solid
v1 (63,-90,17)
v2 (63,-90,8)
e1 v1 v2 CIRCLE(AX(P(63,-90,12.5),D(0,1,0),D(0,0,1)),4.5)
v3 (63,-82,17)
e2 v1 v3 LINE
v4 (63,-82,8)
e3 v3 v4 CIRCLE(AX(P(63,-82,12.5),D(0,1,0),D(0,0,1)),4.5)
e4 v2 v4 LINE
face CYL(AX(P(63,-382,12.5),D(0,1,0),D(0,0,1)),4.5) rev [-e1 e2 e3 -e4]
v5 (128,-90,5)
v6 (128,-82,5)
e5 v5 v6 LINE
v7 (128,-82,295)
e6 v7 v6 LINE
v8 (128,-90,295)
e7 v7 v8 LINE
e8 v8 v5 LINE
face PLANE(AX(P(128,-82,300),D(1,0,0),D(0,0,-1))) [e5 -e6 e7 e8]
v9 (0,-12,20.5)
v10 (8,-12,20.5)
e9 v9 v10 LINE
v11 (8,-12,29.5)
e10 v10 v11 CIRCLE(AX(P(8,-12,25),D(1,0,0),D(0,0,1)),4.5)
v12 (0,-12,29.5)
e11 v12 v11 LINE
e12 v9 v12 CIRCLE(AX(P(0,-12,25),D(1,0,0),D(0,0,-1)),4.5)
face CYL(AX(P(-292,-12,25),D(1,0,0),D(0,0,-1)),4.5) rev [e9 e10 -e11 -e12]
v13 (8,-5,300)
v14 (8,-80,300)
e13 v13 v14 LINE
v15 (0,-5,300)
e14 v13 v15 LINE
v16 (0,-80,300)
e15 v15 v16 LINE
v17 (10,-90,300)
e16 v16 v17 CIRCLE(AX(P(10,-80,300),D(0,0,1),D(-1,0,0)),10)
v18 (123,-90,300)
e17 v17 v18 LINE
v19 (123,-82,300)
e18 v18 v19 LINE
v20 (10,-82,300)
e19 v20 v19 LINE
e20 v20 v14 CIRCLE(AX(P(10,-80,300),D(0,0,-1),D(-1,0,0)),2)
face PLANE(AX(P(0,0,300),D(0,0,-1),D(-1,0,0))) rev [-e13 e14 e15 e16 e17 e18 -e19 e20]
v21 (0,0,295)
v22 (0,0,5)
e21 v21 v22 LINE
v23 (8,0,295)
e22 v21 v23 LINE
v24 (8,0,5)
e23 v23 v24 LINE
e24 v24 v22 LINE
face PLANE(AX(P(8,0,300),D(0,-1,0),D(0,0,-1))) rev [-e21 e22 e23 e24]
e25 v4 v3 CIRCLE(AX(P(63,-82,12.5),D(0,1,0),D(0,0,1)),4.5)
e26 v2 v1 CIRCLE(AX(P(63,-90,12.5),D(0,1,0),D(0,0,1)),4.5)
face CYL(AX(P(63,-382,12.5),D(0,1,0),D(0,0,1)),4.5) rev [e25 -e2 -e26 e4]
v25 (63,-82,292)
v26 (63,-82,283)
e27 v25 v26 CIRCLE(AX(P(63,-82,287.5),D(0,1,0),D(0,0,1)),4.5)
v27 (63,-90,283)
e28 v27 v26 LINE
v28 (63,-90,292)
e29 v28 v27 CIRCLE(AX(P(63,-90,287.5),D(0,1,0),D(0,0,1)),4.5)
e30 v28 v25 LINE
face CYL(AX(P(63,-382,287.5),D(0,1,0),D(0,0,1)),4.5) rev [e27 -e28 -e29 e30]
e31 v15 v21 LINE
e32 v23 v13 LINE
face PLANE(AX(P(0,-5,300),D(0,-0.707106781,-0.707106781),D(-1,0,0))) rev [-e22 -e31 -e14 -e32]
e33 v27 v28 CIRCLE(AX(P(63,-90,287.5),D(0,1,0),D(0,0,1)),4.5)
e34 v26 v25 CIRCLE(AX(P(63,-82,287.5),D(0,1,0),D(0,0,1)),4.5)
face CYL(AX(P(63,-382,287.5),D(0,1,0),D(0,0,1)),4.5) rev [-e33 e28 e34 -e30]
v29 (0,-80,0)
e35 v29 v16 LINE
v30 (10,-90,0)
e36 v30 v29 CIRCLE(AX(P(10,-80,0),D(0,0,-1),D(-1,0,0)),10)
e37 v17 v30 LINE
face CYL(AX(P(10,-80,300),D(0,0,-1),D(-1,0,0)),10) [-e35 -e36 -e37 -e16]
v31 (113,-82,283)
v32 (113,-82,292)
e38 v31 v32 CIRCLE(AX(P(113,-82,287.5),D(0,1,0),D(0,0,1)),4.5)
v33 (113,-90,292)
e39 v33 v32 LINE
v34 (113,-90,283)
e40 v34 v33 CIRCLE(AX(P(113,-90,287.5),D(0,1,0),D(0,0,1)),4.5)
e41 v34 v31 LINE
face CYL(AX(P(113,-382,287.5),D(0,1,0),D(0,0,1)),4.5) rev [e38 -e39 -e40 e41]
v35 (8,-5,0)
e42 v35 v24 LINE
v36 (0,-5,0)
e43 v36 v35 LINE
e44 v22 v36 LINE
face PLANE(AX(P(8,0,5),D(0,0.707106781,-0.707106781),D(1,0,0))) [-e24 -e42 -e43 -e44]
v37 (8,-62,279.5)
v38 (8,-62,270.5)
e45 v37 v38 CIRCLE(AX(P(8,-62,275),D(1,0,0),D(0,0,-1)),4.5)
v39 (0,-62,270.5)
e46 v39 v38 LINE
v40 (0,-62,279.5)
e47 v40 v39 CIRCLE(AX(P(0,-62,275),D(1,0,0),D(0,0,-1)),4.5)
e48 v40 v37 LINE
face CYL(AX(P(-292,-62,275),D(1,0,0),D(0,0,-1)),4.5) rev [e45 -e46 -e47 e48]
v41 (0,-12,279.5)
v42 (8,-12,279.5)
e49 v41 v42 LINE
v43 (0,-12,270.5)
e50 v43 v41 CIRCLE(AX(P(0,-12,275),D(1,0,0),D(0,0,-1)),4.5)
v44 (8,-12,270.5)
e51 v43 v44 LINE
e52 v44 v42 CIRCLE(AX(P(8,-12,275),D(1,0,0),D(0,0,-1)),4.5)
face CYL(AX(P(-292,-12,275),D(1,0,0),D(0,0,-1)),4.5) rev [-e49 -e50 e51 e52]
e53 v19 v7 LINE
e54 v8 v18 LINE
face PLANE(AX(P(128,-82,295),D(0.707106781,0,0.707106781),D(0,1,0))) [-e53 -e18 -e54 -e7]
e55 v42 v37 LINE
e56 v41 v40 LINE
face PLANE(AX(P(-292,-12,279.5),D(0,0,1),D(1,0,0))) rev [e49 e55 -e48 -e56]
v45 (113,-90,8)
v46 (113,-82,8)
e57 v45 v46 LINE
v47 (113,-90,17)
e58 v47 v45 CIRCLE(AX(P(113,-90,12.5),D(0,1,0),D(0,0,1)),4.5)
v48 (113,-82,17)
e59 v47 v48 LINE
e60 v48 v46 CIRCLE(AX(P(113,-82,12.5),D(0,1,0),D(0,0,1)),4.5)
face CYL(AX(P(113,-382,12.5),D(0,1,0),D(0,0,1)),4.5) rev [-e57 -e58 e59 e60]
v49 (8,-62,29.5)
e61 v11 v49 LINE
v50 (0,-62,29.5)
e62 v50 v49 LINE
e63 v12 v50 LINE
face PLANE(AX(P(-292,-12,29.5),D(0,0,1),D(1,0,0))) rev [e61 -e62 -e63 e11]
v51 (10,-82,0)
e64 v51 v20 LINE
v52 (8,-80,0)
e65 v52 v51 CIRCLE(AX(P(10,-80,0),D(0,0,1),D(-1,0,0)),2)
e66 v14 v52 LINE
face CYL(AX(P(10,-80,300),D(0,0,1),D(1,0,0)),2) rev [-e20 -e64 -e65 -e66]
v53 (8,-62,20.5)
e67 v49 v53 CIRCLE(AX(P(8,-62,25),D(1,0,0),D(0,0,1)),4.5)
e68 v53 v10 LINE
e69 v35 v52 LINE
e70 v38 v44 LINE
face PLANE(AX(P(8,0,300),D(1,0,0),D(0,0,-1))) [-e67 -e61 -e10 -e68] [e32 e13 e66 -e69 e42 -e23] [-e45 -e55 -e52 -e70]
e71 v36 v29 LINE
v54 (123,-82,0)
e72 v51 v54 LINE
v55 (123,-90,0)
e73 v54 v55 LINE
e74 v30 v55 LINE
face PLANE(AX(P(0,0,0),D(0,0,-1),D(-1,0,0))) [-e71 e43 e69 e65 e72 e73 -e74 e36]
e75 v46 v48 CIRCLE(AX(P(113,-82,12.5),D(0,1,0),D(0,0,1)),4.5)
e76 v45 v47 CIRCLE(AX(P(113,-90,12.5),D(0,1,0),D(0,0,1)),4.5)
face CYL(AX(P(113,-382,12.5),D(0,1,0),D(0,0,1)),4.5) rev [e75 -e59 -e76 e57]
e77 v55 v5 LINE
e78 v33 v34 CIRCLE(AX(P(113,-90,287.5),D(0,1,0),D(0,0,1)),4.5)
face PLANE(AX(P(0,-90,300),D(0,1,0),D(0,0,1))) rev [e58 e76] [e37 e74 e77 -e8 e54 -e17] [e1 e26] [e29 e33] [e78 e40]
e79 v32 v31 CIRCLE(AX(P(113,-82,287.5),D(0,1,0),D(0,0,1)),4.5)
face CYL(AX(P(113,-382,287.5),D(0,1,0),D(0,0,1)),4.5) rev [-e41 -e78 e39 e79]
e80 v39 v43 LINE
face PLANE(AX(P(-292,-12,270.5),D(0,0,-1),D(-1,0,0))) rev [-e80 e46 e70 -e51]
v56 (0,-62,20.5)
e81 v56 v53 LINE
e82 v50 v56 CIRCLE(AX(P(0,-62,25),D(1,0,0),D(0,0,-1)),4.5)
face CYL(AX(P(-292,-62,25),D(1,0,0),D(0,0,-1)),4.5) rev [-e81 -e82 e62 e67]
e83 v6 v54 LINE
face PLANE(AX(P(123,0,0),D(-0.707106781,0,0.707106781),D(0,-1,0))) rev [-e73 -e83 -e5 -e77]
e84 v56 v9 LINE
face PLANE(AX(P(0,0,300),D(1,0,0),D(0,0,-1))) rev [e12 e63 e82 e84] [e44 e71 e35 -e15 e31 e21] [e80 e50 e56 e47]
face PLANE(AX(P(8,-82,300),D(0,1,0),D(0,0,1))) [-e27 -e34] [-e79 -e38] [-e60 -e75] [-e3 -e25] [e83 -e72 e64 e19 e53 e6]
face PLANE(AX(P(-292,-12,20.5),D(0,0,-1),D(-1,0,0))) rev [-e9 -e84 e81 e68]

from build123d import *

# Parameters (mm, degrees)
BOSS_EXTRUDE1_DEPTH = 300
SKETCH2_R           = 4.5
CUT_EXTRUDE1_DEPTH  = 300
CUT_EXTRUDE2_DEPTH  = 300
CHAMFER1_SIZE       = 5
FILLET1_R           = 2
FILLET2_R           = 10


with BuildPart() as part:
    # Sketch1 → Boss-Extrude1 (new body)
    with BuildSketch(Plane.XY):
        Polygon((0, 0), (0, -90), (128, -90), (128, -82), (8, -82), (8, 0), align=None)
    extrude(amount=BOSS_EXTRUDE1_DEPTH)

    # Sketch2 → Cut-Extrude1 (cut)
    with BuildSketch(Plane(origin=(0, -82, 0), x_dir=(1, 0, 0), z_dir=(0, 1, 0))):
        with Locations(Location((63, -12.5, 0), (0, 0, 270))):
            Circle(SKETCH2_R)
        with Locations(Location((113, -12.5, 0), (0, 0, 270))):
            Circle(SKETCH2_R)
        with Locations(Location((63, -287.5, 0), (0, 0, 270))):
            Circle(SKETCH2_R)
        with Locations(Location((113, -287.5, 0), (0, 0, 270))):
            Circle(SKETCH2_R)
    extrude(amount=-CUT_EXTRUDE1_DEPTH, mode=Mode.SUBTRACT)

    # Sketch3 → Cut-Extrude2 (cut)
    with BuildSketch(Plane(origin=(8, 0, 0), x_dir=(0, 0, -1), z_dir=(1, 0, 0))):
        with BuildLine():
            Line((-270.5, -12), (-270.5, -62))
            ThreePointArc((-270.5, -62), (-275, -66.5), (-279.5, -62))
            Line((-279.5, -62), (-279.5, -12))
            ThreePointArc((-279.5, -12), (-275, -7.5), (-270.5, -12))
        make_face()
        with BuildLine():
            Line((-29.5, -12), (-29.5, -62))
            ThreePointArc((-29.5, -62), (-25, -66.5), (-20.5, -62))
            Line((-20.5, -62), (-20.5, -12))
            ThreePointArc((-20.5, -12), (-25, -7.5), (-29.5, -12))
        make_face()
    extrude(amount=-CUT_EXTRUDE2_DEPTH, mode=Mode.SUBTRACT)

    # Chamfer1
    chamfer1_edges = [part.edges().sort_by_distance(p)[0] for p in [
        (4, 0, 300),
        (4, 0, 0),
        (128, -86, 0),
        (128, -86, 300),
    ]]
    chamfer(chamfer1_edges, length=CHAMFER1_SIZE)

    # Fillet1
    fillet1_edges = [part.edges().sort_by_distance(p)[0] for p in [
        (8, -82, 150),
    ]]
    fillet(fillet1_edges, radius=FILLET1_R)

    # Fillet2
    fillet2_edges = [part.edges().sort_by_distance(p)[0] for p in [
        (0, -90, 150),
    ]]
    fillet(fillet2_edges, radius=FILLET2_R)


solid = part.part
